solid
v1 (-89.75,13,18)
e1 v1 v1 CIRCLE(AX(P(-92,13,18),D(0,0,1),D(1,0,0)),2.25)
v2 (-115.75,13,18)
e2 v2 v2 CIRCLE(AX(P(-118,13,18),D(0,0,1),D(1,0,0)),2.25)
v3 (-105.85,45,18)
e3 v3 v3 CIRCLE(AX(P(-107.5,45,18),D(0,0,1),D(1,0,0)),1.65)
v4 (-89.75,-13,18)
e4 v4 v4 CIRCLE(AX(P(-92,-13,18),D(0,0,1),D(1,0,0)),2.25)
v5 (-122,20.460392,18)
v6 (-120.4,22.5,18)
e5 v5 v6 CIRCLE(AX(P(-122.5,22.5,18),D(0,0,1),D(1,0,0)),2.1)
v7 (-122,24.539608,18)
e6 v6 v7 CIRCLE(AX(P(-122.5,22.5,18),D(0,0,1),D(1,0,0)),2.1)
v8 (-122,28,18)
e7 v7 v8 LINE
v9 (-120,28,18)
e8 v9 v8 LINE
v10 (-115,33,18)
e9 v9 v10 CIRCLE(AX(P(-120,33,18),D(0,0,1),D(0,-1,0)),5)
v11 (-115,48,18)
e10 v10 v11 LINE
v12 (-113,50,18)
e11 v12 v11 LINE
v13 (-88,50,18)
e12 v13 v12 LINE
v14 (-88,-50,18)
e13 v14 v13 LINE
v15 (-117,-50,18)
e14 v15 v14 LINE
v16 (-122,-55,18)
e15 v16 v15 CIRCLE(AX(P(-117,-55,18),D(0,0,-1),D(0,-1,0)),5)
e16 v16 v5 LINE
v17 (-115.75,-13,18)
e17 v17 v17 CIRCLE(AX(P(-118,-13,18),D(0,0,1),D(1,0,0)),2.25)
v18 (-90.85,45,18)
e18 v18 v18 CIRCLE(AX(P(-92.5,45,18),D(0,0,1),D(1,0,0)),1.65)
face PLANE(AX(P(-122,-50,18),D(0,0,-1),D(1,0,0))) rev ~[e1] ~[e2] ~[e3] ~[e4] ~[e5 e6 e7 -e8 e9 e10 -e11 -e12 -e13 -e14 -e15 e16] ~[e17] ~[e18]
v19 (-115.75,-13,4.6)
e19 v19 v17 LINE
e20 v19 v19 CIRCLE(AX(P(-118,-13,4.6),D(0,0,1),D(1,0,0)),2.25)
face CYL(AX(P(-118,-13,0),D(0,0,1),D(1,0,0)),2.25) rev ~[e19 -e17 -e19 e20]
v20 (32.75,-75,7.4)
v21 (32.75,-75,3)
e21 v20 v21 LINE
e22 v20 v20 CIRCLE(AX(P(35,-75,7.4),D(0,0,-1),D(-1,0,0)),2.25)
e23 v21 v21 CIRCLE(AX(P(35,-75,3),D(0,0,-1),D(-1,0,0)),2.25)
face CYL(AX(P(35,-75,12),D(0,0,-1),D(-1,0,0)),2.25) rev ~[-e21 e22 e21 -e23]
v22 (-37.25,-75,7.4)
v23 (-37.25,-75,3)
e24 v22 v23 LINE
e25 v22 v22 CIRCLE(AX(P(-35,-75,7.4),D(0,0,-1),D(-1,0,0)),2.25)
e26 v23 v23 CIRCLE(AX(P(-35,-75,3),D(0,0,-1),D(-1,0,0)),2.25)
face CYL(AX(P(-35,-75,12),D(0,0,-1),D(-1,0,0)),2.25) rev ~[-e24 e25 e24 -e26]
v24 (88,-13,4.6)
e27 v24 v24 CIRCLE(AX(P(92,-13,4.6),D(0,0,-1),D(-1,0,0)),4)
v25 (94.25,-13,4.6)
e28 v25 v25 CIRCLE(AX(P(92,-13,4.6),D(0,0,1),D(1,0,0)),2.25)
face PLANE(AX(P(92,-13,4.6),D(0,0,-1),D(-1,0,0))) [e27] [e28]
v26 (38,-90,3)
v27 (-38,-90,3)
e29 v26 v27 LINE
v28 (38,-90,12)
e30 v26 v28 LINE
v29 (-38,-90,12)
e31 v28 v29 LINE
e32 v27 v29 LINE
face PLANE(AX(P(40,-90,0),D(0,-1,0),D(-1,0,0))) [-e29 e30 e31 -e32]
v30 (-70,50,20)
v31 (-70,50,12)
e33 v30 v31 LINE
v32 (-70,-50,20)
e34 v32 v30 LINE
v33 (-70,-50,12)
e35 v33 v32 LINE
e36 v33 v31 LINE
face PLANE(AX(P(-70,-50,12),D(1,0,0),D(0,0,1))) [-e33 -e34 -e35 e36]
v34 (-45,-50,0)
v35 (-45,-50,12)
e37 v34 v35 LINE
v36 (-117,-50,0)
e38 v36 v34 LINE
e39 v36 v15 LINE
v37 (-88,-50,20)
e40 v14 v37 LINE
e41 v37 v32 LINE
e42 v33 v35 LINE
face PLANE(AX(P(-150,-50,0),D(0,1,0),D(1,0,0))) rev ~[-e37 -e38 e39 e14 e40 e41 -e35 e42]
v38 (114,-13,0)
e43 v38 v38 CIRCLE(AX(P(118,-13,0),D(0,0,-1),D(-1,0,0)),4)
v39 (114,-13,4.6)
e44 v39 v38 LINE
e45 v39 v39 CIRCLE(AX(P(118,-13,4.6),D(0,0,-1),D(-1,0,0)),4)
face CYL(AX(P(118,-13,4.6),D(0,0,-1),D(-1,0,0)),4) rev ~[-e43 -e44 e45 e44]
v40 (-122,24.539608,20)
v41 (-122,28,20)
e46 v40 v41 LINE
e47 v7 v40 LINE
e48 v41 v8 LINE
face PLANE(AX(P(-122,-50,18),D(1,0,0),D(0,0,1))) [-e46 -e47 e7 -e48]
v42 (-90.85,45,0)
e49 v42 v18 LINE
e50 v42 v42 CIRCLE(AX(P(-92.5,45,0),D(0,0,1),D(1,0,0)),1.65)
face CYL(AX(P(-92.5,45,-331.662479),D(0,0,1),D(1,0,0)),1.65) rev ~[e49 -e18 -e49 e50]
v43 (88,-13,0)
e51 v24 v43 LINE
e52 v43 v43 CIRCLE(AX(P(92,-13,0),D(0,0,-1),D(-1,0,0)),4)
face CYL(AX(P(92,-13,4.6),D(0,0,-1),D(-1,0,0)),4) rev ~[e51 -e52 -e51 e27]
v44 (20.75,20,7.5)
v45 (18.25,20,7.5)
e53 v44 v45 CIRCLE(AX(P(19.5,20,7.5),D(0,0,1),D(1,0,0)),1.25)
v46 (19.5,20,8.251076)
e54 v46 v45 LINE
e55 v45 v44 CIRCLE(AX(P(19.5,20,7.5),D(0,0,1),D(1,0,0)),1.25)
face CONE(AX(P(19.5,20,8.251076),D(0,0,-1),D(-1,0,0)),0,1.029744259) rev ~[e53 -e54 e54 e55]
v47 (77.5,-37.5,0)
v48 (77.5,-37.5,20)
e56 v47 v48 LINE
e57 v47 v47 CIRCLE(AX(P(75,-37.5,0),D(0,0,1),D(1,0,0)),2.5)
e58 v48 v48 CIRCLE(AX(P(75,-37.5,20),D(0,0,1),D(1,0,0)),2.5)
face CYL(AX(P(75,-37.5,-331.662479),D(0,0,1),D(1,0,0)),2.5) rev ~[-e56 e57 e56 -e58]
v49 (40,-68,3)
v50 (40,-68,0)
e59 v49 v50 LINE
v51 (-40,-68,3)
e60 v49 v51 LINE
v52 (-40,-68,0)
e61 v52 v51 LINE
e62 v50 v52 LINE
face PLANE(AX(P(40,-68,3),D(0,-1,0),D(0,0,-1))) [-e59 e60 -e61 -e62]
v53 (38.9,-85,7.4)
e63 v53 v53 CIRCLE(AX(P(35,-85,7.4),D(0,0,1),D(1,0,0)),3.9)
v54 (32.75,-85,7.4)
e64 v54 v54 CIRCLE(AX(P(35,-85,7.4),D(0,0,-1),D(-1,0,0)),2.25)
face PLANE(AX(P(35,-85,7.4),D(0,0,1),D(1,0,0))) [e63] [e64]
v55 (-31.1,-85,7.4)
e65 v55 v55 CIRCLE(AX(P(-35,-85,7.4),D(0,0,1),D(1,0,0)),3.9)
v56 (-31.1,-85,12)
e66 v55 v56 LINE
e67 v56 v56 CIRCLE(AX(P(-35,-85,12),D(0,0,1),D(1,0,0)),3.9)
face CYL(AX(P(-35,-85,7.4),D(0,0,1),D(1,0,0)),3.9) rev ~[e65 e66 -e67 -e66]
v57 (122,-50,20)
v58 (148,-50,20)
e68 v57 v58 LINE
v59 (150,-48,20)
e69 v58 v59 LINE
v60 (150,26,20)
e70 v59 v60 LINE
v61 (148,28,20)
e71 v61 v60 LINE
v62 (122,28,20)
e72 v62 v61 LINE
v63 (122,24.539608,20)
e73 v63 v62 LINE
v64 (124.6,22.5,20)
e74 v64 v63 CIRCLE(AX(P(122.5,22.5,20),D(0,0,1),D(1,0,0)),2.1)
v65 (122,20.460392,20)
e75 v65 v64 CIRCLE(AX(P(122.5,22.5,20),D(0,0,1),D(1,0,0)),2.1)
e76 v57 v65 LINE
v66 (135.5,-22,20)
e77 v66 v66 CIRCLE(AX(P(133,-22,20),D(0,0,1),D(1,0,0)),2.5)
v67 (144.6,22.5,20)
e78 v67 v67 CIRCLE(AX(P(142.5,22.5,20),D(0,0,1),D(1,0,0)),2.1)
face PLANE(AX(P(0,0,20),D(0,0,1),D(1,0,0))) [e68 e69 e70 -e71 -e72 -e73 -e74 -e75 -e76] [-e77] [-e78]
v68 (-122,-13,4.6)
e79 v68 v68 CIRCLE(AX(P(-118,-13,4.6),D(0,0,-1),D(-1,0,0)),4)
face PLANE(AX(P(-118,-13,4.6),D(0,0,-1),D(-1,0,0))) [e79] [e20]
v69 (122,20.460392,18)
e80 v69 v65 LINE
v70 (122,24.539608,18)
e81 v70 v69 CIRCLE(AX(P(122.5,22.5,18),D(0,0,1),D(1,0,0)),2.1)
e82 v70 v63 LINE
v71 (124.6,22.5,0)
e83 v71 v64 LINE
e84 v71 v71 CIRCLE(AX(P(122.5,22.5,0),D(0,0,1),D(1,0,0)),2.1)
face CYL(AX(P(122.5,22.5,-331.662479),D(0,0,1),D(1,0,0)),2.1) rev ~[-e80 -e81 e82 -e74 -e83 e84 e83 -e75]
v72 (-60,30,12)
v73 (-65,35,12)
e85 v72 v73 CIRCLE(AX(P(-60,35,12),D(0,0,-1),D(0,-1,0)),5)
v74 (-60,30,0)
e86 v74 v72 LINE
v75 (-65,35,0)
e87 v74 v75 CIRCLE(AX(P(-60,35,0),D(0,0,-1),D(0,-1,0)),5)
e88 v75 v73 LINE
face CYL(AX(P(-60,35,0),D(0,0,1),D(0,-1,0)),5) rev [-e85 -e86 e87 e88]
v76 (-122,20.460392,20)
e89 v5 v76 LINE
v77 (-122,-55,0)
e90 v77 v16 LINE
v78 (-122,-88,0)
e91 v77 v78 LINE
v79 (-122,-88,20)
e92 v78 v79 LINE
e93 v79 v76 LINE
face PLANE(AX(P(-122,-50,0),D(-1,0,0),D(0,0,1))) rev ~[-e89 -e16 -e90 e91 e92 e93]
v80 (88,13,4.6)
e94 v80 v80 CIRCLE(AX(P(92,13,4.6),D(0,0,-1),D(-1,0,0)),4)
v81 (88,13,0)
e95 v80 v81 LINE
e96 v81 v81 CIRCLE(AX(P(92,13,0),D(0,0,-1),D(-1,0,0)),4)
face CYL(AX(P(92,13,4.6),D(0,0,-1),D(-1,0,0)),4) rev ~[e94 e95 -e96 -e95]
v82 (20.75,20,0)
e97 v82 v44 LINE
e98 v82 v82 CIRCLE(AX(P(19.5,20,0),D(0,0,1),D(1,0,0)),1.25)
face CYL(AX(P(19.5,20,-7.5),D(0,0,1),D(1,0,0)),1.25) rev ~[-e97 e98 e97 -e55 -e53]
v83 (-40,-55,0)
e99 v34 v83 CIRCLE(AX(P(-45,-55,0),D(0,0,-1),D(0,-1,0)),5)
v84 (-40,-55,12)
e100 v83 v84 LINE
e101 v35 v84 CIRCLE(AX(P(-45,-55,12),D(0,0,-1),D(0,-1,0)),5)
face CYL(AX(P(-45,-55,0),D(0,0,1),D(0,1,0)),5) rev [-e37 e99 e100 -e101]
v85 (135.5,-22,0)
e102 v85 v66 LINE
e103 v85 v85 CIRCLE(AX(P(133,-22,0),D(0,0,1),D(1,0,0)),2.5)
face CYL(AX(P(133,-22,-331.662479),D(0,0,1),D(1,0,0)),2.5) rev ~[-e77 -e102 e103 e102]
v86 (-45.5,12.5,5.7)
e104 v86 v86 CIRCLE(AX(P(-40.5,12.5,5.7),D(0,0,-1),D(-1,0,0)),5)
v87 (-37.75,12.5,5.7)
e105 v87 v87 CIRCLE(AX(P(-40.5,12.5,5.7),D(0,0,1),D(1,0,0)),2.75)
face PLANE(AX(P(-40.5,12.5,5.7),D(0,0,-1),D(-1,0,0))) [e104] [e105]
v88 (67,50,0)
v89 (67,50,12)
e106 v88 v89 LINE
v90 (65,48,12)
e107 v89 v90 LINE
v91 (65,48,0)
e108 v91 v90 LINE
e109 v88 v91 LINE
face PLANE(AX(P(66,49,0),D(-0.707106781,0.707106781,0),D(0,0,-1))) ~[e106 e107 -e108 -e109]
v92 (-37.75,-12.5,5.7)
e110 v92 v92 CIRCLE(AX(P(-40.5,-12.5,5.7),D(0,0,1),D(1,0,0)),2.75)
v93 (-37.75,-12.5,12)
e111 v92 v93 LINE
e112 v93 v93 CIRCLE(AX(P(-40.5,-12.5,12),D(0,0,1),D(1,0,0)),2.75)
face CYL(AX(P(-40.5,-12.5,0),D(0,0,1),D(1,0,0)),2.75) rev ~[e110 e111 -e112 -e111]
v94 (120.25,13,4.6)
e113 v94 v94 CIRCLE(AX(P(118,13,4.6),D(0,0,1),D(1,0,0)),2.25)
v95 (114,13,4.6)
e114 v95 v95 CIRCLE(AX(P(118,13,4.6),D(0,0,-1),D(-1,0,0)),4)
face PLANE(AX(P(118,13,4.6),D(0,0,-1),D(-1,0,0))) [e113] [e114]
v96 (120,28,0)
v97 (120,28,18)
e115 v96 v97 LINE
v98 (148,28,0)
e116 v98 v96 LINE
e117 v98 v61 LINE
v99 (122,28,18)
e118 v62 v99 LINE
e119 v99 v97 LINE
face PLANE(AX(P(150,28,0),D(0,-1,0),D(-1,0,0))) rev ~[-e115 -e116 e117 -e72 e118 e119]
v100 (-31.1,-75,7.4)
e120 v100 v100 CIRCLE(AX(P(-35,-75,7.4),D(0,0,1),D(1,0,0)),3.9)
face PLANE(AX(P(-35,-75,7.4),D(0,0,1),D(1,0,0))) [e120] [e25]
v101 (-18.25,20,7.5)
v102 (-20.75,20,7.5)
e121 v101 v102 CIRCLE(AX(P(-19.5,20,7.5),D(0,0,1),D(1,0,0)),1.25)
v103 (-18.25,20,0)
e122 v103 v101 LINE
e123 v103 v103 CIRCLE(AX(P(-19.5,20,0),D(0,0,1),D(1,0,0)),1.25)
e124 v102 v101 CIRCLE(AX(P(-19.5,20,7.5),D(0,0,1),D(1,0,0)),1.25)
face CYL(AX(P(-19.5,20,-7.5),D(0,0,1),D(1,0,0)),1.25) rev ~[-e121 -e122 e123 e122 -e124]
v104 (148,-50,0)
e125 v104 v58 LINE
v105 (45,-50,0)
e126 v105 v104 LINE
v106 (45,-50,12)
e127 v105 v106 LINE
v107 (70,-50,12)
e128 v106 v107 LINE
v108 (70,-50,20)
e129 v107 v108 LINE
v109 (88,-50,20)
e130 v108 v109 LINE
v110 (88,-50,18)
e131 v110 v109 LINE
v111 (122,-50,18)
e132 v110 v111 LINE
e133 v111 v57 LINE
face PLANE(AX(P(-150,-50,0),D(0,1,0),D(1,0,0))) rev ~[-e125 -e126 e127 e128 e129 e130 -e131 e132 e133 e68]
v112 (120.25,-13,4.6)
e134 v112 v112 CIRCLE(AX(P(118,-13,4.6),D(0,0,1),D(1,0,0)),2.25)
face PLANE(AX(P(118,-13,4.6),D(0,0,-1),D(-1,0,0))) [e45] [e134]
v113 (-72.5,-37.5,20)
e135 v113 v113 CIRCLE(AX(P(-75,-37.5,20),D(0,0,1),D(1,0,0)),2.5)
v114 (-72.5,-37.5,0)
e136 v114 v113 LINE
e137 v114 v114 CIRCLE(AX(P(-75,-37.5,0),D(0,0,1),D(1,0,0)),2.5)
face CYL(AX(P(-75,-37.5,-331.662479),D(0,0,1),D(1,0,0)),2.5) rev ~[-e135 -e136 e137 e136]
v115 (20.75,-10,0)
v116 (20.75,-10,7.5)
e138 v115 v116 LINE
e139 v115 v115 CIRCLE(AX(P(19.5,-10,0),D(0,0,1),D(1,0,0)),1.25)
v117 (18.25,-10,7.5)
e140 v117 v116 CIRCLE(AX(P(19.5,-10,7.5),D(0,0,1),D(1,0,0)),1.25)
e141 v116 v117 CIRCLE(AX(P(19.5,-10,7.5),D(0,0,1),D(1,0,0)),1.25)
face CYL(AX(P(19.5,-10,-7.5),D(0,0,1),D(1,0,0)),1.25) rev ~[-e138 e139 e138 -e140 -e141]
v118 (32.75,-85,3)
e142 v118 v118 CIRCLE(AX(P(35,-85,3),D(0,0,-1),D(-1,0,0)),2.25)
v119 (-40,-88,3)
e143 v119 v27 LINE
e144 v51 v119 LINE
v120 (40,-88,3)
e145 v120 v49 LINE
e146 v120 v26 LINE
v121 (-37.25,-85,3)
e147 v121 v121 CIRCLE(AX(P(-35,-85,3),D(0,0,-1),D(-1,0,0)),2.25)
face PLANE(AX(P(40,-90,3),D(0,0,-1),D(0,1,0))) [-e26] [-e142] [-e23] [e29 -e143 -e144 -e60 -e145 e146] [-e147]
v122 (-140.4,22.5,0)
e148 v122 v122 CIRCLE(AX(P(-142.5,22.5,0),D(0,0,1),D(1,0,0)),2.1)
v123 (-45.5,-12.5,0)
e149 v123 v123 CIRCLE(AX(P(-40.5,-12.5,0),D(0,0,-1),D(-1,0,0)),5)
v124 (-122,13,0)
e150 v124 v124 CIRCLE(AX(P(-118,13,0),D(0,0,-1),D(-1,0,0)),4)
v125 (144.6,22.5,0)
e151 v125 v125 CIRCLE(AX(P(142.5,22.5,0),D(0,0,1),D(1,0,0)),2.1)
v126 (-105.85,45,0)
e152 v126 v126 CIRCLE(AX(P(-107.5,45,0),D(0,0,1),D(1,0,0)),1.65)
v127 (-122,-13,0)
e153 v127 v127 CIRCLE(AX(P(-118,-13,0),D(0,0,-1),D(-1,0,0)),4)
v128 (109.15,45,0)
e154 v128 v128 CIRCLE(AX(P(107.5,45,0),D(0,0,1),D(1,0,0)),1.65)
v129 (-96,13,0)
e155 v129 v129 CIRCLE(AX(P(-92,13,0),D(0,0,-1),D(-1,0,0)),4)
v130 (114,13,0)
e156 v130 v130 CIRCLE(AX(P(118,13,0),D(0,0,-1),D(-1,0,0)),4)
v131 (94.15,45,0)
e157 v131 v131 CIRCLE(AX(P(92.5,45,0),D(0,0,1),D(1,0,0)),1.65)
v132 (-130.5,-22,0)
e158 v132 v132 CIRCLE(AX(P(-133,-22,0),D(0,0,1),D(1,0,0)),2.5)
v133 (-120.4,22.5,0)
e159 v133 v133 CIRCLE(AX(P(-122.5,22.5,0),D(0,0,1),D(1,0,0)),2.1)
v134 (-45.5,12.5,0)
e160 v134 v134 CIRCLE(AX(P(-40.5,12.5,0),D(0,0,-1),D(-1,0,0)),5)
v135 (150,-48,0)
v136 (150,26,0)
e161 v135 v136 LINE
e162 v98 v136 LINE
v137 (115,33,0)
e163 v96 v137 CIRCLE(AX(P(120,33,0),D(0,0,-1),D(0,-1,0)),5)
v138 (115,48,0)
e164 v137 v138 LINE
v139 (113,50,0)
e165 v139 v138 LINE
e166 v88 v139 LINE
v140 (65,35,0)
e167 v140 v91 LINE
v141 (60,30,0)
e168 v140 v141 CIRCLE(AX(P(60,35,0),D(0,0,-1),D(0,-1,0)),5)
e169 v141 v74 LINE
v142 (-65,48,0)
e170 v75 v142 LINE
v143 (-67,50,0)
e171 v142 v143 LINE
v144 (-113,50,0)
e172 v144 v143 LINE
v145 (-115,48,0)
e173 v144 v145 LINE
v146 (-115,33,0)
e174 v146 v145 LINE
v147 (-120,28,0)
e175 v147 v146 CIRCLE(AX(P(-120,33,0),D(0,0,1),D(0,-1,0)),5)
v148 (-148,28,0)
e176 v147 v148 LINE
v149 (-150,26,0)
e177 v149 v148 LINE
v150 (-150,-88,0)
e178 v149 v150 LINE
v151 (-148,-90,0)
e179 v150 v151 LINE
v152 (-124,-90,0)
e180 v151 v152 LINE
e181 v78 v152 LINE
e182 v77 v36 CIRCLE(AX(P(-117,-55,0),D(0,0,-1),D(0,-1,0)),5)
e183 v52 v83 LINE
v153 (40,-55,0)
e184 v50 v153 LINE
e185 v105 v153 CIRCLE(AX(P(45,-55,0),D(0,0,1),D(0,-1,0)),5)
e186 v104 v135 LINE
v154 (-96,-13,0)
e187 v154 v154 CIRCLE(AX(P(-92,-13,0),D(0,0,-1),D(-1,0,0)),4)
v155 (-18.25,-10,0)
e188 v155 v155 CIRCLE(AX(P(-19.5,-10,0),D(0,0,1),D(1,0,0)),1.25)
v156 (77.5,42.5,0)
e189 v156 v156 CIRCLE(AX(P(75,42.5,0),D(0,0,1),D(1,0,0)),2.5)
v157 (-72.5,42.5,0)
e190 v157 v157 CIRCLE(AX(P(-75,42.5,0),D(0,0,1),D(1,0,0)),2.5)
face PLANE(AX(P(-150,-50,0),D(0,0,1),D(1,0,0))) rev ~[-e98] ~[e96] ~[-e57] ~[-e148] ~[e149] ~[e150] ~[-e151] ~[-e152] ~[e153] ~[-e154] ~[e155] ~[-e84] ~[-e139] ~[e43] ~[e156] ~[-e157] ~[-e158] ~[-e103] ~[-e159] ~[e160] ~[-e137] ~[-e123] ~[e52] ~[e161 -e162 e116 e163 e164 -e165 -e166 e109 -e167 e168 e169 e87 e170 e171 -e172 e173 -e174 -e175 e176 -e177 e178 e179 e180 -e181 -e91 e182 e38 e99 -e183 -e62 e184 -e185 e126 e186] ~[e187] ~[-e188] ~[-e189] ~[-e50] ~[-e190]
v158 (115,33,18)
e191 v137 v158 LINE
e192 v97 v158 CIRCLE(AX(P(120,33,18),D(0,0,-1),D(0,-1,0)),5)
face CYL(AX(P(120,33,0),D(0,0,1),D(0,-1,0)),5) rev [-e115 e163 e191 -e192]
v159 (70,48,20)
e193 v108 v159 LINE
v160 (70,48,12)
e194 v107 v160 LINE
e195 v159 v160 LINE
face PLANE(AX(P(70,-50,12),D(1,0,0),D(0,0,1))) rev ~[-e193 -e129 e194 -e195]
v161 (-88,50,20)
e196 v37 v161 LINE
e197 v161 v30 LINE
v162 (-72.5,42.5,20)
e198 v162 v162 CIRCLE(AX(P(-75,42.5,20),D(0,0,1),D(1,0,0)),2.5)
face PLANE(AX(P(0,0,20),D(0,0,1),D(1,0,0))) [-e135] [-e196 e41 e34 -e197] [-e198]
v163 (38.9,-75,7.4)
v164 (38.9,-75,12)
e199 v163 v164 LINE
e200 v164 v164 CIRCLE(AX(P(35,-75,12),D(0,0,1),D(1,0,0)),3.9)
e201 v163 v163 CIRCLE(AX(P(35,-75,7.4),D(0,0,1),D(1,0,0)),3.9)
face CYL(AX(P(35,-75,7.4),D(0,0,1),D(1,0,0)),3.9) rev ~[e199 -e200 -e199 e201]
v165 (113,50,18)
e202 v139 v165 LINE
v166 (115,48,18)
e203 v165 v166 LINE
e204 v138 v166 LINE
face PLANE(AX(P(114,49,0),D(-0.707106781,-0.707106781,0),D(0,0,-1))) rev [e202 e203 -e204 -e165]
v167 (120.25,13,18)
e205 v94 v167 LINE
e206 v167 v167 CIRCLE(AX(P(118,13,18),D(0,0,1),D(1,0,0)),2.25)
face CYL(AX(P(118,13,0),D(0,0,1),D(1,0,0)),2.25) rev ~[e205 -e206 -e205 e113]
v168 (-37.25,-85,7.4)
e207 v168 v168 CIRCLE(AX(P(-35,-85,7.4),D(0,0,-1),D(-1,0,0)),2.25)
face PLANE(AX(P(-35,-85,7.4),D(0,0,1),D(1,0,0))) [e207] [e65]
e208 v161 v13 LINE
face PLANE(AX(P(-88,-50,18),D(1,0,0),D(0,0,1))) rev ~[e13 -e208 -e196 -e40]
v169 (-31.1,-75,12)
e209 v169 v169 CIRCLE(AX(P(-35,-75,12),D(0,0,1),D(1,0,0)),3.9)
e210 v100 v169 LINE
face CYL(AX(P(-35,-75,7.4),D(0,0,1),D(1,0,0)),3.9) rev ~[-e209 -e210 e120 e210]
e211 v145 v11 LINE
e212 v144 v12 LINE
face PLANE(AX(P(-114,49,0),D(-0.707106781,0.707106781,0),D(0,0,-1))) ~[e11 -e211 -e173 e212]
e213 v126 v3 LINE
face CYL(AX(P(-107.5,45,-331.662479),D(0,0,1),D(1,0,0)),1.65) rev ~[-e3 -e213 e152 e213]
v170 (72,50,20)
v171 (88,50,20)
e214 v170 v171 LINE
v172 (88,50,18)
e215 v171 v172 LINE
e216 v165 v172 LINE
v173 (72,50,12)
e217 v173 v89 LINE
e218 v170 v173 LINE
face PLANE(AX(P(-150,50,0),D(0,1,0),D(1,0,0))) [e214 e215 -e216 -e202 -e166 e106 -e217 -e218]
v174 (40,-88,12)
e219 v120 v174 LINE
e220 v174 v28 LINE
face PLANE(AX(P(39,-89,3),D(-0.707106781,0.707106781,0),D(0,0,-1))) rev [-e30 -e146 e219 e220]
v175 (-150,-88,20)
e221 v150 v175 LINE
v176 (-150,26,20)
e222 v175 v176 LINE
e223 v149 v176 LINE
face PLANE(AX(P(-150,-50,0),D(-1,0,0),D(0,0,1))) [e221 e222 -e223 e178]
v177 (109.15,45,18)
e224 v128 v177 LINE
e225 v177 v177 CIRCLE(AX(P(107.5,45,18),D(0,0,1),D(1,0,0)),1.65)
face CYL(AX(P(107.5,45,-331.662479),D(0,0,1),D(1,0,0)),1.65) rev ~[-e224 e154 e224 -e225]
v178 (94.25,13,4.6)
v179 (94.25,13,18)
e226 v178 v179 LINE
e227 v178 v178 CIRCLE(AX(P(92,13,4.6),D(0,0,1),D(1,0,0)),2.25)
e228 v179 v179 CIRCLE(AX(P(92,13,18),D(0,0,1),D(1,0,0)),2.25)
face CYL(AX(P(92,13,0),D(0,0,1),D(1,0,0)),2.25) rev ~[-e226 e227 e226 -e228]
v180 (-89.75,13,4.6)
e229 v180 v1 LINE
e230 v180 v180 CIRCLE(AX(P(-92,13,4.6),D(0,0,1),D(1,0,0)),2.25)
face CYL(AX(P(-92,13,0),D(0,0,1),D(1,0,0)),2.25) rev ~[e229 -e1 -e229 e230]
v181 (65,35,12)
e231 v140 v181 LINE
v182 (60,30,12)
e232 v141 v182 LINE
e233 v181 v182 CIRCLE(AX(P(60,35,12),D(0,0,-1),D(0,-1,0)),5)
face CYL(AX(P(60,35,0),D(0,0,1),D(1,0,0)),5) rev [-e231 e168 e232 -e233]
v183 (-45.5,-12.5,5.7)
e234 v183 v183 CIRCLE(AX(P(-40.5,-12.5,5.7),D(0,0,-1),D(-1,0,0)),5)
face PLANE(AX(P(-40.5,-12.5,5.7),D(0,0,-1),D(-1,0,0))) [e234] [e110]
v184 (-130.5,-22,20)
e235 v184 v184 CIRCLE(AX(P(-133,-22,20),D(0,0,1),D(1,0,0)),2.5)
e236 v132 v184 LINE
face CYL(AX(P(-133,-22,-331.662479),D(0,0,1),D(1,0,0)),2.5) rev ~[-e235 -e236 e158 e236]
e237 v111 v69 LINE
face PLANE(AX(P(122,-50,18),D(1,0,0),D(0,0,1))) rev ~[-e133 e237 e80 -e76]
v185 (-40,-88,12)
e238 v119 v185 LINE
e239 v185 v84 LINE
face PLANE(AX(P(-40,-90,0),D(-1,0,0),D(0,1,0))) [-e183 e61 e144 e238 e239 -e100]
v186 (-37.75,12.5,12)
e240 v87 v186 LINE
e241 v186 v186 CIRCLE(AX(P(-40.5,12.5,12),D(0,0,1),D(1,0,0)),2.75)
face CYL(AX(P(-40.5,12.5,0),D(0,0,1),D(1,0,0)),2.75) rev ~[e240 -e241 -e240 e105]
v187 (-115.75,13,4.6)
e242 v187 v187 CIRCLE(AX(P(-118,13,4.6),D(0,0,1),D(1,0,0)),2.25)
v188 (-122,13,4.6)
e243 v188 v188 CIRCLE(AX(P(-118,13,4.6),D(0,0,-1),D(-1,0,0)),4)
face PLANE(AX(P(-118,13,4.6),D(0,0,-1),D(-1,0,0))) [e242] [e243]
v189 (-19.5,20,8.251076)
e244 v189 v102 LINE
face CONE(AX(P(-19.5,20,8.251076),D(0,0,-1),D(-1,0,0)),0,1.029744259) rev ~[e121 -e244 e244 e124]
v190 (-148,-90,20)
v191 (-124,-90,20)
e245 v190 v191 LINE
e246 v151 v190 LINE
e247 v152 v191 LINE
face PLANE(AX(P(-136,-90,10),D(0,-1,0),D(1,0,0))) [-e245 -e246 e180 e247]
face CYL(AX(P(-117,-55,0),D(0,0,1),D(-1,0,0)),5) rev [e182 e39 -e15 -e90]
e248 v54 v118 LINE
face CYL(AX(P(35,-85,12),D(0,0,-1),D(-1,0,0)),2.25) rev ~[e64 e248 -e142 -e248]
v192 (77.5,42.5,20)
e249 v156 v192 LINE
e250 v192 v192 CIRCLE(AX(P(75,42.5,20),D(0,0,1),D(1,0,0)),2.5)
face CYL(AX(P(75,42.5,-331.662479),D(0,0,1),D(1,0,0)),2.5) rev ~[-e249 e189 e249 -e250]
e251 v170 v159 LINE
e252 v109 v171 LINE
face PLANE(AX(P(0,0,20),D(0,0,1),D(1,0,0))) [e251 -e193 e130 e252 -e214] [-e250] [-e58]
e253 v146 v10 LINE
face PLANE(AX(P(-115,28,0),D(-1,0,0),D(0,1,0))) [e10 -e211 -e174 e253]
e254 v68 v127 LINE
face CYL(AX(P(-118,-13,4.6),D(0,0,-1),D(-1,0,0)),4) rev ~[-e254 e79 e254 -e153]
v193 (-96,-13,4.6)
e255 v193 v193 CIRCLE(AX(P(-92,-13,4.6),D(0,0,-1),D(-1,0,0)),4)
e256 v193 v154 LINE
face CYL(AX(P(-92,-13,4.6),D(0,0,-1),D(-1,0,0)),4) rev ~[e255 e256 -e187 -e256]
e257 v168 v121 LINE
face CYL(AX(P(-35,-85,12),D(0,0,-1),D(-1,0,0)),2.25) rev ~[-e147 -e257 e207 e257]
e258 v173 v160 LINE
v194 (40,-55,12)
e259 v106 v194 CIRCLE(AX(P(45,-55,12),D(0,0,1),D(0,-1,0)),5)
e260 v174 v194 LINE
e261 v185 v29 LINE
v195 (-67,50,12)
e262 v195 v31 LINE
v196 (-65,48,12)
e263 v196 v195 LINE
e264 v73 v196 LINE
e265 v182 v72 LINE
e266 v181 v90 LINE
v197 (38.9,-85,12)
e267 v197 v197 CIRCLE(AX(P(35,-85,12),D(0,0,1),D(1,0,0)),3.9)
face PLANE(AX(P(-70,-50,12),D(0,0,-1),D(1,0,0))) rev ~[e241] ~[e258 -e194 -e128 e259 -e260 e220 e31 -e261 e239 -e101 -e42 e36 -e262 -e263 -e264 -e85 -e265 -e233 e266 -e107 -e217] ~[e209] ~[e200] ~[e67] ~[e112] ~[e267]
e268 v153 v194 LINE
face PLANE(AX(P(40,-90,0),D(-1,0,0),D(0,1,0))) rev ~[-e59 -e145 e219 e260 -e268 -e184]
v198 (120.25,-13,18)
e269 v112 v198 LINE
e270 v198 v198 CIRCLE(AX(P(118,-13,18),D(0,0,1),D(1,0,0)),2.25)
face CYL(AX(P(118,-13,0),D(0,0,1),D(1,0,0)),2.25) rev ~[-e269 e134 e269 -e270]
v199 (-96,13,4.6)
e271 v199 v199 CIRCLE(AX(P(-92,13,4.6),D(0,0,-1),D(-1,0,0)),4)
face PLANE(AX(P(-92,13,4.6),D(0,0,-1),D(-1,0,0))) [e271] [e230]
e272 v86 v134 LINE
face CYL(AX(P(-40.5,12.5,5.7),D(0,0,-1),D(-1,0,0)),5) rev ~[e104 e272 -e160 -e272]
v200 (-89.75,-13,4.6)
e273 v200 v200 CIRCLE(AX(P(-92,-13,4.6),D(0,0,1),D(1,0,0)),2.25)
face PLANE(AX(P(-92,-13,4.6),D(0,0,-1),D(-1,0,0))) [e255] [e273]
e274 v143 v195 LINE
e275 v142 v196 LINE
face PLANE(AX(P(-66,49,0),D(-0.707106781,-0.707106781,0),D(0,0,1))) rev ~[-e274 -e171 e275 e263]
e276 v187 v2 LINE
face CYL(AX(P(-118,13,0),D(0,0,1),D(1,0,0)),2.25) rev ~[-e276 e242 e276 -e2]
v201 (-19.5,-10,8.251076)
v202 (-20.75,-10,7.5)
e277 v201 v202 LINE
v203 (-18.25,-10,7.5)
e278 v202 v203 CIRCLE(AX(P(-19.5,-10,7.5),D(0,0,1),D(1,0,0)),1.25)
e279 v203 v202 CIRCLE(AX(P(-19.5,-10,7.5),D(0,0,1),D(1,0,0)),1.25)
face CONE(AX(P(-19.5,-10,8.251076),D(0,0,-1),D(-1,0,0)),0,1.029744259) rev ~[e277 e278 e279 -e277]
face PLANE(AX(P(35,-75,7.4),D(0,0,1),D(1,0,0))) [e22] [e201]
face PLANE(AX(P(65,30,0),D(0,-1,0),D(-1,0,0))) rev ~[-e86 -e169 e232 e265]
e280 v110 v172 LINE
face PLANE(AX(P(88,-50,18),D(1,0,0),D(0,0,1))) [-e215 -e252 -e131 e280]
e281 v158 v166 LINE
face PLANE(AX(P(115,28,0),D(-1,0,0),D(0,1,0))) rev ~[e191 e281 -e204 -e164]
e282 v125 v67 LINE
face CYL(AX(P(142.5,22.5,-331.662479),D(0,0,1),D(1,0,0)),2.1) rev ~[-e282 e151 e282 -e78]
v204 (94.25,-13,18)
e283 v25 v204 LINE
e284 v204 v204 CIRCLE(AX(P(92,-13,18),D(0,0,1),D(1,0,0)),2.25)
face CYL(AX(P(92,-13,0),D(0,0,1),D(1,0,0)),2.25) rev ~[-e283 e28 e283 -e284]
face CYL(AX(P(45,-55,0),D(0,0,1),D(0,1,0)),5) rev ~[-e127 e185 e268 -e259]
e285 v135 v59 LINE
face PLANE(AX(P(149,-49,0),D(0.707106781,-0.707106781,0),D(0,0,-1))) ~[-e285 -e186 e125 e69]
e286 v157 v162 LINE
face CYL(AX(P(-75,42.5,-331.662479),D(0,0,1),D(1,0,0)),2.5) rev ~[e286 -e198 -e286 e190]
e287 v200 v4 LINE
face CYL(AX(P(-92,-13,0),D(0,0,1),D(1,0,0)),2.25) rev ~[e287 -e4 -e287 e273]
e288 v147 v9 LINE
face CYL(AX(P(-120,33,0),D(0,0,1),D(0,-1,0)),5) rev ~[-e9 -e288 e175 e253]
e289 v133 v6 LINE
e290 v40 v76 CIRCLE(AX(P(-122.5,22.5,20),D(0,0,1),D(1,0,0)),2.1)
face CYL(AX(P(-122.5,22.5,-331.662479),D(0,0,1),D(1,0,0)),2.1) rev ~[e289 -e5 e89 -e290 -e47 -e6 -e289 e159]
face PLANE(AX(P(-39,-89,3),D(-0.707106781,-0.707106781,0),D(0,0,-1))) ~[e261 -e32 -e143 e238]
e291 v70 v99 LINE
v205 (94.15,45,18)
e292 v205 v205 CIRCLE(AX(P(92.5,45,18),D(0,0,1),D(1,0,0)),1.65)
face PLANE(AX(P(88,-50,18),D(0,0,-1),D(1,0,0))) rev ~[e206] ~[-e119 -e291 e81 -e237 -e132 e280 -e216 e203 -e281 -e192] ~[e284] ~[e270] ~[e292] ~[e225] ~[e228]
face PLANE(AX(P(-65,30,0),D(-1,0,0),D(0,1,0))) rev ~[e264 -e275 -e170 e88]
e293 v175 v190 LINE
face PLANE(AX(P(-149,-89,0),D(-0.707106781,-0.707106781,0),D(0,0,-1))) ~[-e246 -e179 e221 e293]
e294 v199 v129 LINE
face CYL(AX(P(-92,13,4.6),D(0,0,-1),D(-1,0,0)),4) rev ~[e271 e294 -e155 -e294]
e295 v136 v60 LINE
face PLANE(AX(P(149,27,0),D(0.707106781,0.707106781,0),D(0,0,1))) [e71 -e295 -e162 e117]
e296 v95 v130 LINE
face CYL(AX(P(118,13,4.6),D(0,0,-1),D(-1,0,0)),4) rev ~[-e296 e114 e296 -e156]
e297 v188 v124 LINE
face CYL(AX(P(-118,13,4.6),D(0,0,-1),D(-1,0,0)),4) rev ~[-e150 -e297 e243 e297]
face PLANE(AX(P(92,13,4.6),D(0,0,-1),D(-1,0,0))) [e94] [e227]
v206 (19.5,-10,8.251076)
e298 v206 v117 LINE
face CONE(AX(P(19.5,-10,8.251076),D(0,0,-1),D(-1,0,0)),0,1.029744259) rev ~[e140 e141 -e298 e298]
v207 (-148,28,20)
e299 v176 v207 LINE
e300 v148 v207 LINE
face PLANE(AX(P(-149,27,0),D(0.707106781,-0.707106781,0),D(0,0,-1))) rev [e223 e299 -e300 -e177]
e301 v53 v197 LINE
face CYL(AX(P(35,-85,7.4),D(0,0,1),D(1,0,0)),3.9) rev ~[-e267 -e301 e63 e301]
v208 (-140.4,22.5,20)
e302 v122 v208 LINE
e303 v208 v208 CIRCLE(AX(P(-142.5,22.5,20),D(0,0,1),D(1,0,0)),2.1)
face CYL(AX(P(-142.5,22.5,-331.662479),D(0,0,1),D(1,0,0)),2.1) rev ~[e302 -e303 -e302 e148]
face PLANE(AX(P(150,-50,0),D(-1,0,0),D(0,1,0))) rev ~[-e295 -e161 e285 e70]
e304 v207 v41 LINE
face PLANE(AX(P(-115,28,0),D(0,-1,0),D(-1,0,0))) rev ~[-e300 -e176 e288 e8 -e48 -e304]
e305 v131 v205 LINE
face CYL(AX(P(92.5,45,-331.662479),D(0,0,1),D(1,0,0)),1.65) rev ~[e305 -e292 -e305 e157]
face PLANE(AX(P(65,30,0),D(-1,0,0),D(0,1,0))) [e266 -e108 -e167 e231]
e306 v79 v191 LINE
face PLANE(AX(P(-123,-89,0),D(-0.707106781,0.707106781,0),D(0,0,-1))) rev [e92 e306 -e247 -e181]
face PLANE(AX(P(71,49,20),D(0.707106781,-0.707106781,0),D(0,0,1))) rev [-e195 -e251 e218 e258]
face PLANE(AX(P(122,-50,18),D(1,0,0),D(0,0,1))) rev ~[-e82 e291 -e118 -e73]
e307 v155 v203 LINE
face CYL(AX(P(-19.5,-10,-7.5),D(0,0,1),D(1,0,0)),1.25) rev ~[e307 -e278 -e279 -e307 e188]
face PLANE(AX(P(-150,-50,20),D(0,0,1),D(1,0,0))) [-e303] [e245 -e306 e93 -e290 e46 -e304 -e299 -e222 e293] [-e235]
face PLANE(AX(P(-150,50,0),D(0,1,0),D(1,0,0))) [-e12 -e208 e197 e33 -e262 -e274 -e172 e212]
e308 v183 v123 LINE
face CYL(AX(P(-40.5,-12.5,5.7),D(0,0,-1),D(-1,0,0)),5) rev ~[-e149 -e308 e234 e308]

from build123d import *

# Parameters (mm, degrees)
SKETCH_1_W                   = 300
SKETCH_1_H                   = 100
EXTRUDE_1_DEPTH              = 20
CHAMFER_1_SIZE               = 2
SKETCH_2_W                   = 34
SKETCH_2_H                   = 2
CUT_EXTRUDE_1_DEPTH          = 182.383571472
SKETCH_3_W                   = 140
SKETCH_3_H                   = 8
CUT_EXTRUDE_2_DEPTH          = 182.383571472
SKETCH_4_W                   = 80
SKETCH_4_H                   = 40
EXTRUDE_2_DEPTH              = 12
FILLET_1_R                   = 5
SKETCH_5_W                   = 3
SKETCH_5_H                   = 22
CUT_EXTRUDE_3_DEPTH          = 212.187120819
CHAMFER_2_SIZE               = 2
SKETCH_6_W                   = 130
SKETCH_6_H                   = 20
CUT_EXTRUDE_4_DEPTH          = 177.068168617
FILLET_2_R                   = 5
HOLE_WIZARD_M6_1_D           = 5
SKETCH_10_W                  = 35
SKETCH_10_H                  = 22
CUT_EXTRUDE_5_DEPTH          = 177.068168617
CHAMFER_3_SIZE               = 2
FILLET_3_R                   = 5
HOLE_WIZARD_M5_1_D           = 5.5
HOLE_WIZARD_M5_1_CBORE_D     = 10
HOLE_WIZARD_M5_1_CBORE_DEPTH = 5.7
HOLE_WIZARD_M4_1_D           = 4.5
HOLE_WIZARD_M4_1_CBORE_D     = 8
HOLE_WIZARD_M4_1_CBORE_DEPTH = 4.6
HOLE_WIZARD_M6_2_D           = 5
HOLE_WIZARD_M3_1_D           = 2.5
HOLE_WIZARD_M3_1_DEPTH       = 7.5
HOLE_WIZARD_M3_1_TIP         = 0.751075774
HOLE_WIZARD_M5_1_2_D         = 4.2
HOLE_WIZARD_M4_3_D           = 4.5
HOLE_WIZARD_M4_3_CBORE_D     = 7.8
HOLE_WIZARD_M4_3_CBORE_DEPTH = 4.6
CHAMFER_4_SIZE               = 2
SKETCH_31_W                  = 28
SKETCH_31_H                  = 20
EXTRUDE_3_DEPTH              = 40
CHAMFER_5_SIZE               = 2
FILLET_4_R                   = 5
HOLE_WIZARD_M4_1_2_D         = 3.3


with BuildPart() as part:
    # 草图1 → 凸台-拉伸1 (new body)
    with BuildSketch(Plane.XY):
        Rectangle(SKETCH_1_W, SKETCH_1_H)
    extrude(amount=EXTRUDE_1_DEPTH)

    # 倒角1
    chamfer_1_edges = [part.edges().sort_by_distance(p)[0] for p in [
        (150, -50, 10),
        (150, 50, 10),
        (-150, 50, 10),
    ]]
    chamfer(chamfer_1_edges, length=CHAMFER_1_SIZE)

    # 草图2 → 切除-拉伸1 (cut, through all)
    with BuildSketch(Plane.XZ.offset(50)):
        with Locations((-105, 19)):
            Rectangle(SKETCH_2_W, SKETCH_2_H)
        with Locations((105, 19)):
            Rectangle(SKETCH_2_W, SKETCH_2_H)
    extrude(amount=-CUT_EXTRUDE_1_DEPTH, mode=Mode.SUBTRACT)

    # 草图3 → 切除-拉伸2 (cut, through all)
    with BuildSketch(Plane.XZ.offset(50)):
        with Locations((0, 16)):
            Rectangle(SKETCH_3_W, SKETCH_3_H)
    extrude(amount=-CUT_EXTRUDE_2_DEPTH, mode=Mode.SUBTRACT)

    # 草图4 → 凸台-拉伸2 (add)
    with BuildSketch(Plane(origin=(0, 0, 0), x_dir=(-1, 0, 0), z_dir=(0, 0, -1))):
        with Locations((0, -70)):
            Rectangle(SKETCH_4_W, SKETCH_4_H)
    extrude(amount=-EXTRUDE_2_DEPTH)

    # 圆角1
    fillet_1_edges = [part.edges().sort_by_distance(p)[0] for p in [
        (40, -50, 6),
        (-40, -50, 6),
    ]]
    fillet(fillet_1_edges, radius=FILLET_1_R)

    # 草图5 → 切除-拉伸3 (cut, through all)
    with BuildSketch(Plane(origin=(40, 0, 0), x_dir=(0, 0, -1), z_dir=(1, 0, 0))):
        with Locations((-1.5, -79)):
            Rectangle(SKETCH_5_W, SKETCH_5_H)
    extrude(amount=-CUT_EXTRUDE_3_DEPTH, mode=Mode.SUBTRACT)

    # 倒角2
    chamfer_2_edges = [part.edges().sort_by_distance(p)[0] for p in [
        (40, -90, 7.5),
        (-40, -90, 7.5),
    ]]
    chamfer(chamfer_2_edges, length=CHAMFER_2_SIZE)

    # 草图6 → 切除-拉伸4 (cut, through all)
    with BuildSketch(Plane(origin=(0, 0, 0), x_dir=(-1, 0, 0), z_dir=(0, 0, -1))):
        with Locations((0, 40)):
            Rectangle(SKETCH_6_W, SKETCH_6_H)
    extrude(amount=-CUT_EXTRUDE_4_DEPTH, mode=Mode.SUBTRACT)

    # 圆角2
    fillet_2_edges = [part.edges().sort_by_distance(p)[0] for p in [
        (65, 30, 6),
        (-65, 30, 6),
    ]]
    fillet(fillet_2_edges, radius=FILLET_2_R)

    # M6 螺纹孔1 (through all)
    with Locations(Plane(origin=(0, 0, 0), x_dir=(-1, 0, 0), z_dir=(0, 0, -1))):
        with Locations((133, -22), (-133, -22)):
            Hole(HOLE_WIZARD_M6_1_D / 2)

    # 草图10 → 切除-拉伸5 (cut, through all)
    with BuildSketch(Plane(origin=(0, 0, 0), x_dir=(-1, 0, 0), z_dir=(0, 0, -1))):
        with Locations((132.5, 39)):
            Rectangle(SKETCH_10_W, SKETCH_10_H)
        with Locations((-132.5, 39)):
            Rectangle(SKETCH_10_W, SKETCH_10_H)
    extrude(amount=-CUT_EXTRUDE_5_DEPTH, mode=Mode.SUBTRACT)

    # 倒角3
    chamfer_3_edges = [part.edges().sort_by_distance(p)[0] for p in [
        (-150, 28, 10),
        (-115, 50, 9),
        (115, 50, 9),
        (150, 28, 10),
        (70, 50, 16),
    ]]
    chamfer(chamfer_3_edges, length=CHAMFER_3_SIZE)

    # 圆角3
    fillet_3_edges = [part.edges().sort_by_distance(p)[0] for p in [
        (-115, 28, 9),
        (115, 28, 9),
    ]]
    fillet(fillet_3_edges, radius=FILLET_3_R)

    # Hole Wizard M5 _1 (through all)
    with Locations(Plane(origin=(0, 0, 0), x_dir=(-1, 0, 0), z_dir=(0, 0, -1))):
        with Locations((40.5, 12.5), (40.5, -12.5)):
            CounterBoreHole(HOLE_WIZARD_M5_1_D / 2, HOLE_WIZARD_M5_1_CBORE_D / 2, HOLE_WIZARD_M5_1_CBORE_DEPTH)

    # Hole Wizard M4 _1 (through all)
    with Locations(Plane(origin=(0, 0, 0), x_dir=(-1, 0, 0), z_dir=(0, 0, -1))):
        with Locations((92, 13), (118, 13), (118, -13), (92, -13), (-92, -13), (-118, -13), (-118, 13), (-92, 13)):
            CounterBoreHole(HOLE_WIZARD_M4_1_D / 2, HOLE_WIZARD_M4_1_CBORE_D / 2, HOLE_WIZARD_M4_1_CBORE_DEPTH)

    # M6 螺纹孔2 (through all)
    with Locations(Plane(origin=(0, 0, 0), x_dir=(-1, 0, 0), z_dir=(0, 0, -1))):
        with Locations((75, 42.5), (75, -37.5), (-75, -37.5), (-75, 42.5)):
            Hole(HOLE_WIZARD_M6_2_D / 2)

    # M3 螺纹孔1
    with Locations(Plane(origin=(0, 0, 0), x_dir=(-1, 0, 0), z_dir=(0, 0, -1))):
        with Locations((19.5, 20), (19.5, -10), (-19.5, -10), (-19.5, 20)):
            Hole(HOLE_WIZARD_M3_1_D / 2, depth=HOLE_WIZARD_M3_1_DEPTH)
            with Locations((0, 0, -(HOLE_WIZARD_M3_1_DEPTH + HOLE_WIZARD_M3_1_TIP / 2))):  # 118° drill point
                Cone(0, HOLE_WIZARD_M3_1_D / 2, HOLE_WIZARD_M3_1_TIP, mode=Mode.SUBTRACT)

    # Hole Wizard M5 _1 2 (through all)
    with Locations(Plane(origin=(0, 0, 0), x_dir=(-1, 0, 0), z_dir=(0, 0, -1))):
        with Locations((-142.5, 22.5), (-122.5, 22.5), (122.5, 22.5), (142.5, 22.5)):
            Hole(HOLE_WIZARD_M5_1_2_D / 2)

    # M4 六角圆柱头螺钉的柱形沉头孔3 (through all)
    with Locations(Plane.XY.offset(12)):
        with Locations((-35, -75), (-35, -85), (35, -75), (35, -85)):
            CounterBoreHole(HOLE_WIZARD_M4_3_D / 2, HOLE_WIZARD_M4_3_CBORE_D / 2, HOLE_WIZARD_M4_3_CBORE_DEPTH)

    # 倒角4
    chamfer_4_edges = [part.edges().sort_by_distance(p)[0] for p in [
        (65, 50, 6),
        (-65, 50, 6),
    ]]
    chamfer(chamfer_4_edges, length=CHAMFER_4_SIZE)

    # 草图31 → 凸台-拉伸3 (add)
    with BuildSketch(Plane.XZ.offset(50)):
        with Locations((-136, 10)):
            Rectangle(SKETCH_31_W, SKETCH_31_H)
    extrude(amount=EXTRUDE_3_DEPTH)

    # 倒角5
    chamfer_5_edges = [part.edges().sort_by_distance(p)[0] for p in [
        (-150, -90, 10),
        (-122, -90, 10),
    ]]
    chamfer(chamfer_5_edges, length=CHAMFER_5_SIZE)

    # 圆角4
    fillet_4_edges = [part.edges().sort_by_distance(p)[0] for p in [
        (-122, -50, 9),
    ]]
    fillet(fillet_4_edges, radius=FILLET_4_R)

    # Hole Wizard M4 _1 2 (through all)
    with Locations(Plane(origin=(0, 0, 0), x_dir=(-1, 0, 0), z_dir=(0, 0, -1))):
        with Locations((-107.5, 45), (-92.5, 45), (92.5, 45), (107.5, 45)):
            Hole(HOLE_WIZARD_M4_1_2_D / 2)


solid = part.part
